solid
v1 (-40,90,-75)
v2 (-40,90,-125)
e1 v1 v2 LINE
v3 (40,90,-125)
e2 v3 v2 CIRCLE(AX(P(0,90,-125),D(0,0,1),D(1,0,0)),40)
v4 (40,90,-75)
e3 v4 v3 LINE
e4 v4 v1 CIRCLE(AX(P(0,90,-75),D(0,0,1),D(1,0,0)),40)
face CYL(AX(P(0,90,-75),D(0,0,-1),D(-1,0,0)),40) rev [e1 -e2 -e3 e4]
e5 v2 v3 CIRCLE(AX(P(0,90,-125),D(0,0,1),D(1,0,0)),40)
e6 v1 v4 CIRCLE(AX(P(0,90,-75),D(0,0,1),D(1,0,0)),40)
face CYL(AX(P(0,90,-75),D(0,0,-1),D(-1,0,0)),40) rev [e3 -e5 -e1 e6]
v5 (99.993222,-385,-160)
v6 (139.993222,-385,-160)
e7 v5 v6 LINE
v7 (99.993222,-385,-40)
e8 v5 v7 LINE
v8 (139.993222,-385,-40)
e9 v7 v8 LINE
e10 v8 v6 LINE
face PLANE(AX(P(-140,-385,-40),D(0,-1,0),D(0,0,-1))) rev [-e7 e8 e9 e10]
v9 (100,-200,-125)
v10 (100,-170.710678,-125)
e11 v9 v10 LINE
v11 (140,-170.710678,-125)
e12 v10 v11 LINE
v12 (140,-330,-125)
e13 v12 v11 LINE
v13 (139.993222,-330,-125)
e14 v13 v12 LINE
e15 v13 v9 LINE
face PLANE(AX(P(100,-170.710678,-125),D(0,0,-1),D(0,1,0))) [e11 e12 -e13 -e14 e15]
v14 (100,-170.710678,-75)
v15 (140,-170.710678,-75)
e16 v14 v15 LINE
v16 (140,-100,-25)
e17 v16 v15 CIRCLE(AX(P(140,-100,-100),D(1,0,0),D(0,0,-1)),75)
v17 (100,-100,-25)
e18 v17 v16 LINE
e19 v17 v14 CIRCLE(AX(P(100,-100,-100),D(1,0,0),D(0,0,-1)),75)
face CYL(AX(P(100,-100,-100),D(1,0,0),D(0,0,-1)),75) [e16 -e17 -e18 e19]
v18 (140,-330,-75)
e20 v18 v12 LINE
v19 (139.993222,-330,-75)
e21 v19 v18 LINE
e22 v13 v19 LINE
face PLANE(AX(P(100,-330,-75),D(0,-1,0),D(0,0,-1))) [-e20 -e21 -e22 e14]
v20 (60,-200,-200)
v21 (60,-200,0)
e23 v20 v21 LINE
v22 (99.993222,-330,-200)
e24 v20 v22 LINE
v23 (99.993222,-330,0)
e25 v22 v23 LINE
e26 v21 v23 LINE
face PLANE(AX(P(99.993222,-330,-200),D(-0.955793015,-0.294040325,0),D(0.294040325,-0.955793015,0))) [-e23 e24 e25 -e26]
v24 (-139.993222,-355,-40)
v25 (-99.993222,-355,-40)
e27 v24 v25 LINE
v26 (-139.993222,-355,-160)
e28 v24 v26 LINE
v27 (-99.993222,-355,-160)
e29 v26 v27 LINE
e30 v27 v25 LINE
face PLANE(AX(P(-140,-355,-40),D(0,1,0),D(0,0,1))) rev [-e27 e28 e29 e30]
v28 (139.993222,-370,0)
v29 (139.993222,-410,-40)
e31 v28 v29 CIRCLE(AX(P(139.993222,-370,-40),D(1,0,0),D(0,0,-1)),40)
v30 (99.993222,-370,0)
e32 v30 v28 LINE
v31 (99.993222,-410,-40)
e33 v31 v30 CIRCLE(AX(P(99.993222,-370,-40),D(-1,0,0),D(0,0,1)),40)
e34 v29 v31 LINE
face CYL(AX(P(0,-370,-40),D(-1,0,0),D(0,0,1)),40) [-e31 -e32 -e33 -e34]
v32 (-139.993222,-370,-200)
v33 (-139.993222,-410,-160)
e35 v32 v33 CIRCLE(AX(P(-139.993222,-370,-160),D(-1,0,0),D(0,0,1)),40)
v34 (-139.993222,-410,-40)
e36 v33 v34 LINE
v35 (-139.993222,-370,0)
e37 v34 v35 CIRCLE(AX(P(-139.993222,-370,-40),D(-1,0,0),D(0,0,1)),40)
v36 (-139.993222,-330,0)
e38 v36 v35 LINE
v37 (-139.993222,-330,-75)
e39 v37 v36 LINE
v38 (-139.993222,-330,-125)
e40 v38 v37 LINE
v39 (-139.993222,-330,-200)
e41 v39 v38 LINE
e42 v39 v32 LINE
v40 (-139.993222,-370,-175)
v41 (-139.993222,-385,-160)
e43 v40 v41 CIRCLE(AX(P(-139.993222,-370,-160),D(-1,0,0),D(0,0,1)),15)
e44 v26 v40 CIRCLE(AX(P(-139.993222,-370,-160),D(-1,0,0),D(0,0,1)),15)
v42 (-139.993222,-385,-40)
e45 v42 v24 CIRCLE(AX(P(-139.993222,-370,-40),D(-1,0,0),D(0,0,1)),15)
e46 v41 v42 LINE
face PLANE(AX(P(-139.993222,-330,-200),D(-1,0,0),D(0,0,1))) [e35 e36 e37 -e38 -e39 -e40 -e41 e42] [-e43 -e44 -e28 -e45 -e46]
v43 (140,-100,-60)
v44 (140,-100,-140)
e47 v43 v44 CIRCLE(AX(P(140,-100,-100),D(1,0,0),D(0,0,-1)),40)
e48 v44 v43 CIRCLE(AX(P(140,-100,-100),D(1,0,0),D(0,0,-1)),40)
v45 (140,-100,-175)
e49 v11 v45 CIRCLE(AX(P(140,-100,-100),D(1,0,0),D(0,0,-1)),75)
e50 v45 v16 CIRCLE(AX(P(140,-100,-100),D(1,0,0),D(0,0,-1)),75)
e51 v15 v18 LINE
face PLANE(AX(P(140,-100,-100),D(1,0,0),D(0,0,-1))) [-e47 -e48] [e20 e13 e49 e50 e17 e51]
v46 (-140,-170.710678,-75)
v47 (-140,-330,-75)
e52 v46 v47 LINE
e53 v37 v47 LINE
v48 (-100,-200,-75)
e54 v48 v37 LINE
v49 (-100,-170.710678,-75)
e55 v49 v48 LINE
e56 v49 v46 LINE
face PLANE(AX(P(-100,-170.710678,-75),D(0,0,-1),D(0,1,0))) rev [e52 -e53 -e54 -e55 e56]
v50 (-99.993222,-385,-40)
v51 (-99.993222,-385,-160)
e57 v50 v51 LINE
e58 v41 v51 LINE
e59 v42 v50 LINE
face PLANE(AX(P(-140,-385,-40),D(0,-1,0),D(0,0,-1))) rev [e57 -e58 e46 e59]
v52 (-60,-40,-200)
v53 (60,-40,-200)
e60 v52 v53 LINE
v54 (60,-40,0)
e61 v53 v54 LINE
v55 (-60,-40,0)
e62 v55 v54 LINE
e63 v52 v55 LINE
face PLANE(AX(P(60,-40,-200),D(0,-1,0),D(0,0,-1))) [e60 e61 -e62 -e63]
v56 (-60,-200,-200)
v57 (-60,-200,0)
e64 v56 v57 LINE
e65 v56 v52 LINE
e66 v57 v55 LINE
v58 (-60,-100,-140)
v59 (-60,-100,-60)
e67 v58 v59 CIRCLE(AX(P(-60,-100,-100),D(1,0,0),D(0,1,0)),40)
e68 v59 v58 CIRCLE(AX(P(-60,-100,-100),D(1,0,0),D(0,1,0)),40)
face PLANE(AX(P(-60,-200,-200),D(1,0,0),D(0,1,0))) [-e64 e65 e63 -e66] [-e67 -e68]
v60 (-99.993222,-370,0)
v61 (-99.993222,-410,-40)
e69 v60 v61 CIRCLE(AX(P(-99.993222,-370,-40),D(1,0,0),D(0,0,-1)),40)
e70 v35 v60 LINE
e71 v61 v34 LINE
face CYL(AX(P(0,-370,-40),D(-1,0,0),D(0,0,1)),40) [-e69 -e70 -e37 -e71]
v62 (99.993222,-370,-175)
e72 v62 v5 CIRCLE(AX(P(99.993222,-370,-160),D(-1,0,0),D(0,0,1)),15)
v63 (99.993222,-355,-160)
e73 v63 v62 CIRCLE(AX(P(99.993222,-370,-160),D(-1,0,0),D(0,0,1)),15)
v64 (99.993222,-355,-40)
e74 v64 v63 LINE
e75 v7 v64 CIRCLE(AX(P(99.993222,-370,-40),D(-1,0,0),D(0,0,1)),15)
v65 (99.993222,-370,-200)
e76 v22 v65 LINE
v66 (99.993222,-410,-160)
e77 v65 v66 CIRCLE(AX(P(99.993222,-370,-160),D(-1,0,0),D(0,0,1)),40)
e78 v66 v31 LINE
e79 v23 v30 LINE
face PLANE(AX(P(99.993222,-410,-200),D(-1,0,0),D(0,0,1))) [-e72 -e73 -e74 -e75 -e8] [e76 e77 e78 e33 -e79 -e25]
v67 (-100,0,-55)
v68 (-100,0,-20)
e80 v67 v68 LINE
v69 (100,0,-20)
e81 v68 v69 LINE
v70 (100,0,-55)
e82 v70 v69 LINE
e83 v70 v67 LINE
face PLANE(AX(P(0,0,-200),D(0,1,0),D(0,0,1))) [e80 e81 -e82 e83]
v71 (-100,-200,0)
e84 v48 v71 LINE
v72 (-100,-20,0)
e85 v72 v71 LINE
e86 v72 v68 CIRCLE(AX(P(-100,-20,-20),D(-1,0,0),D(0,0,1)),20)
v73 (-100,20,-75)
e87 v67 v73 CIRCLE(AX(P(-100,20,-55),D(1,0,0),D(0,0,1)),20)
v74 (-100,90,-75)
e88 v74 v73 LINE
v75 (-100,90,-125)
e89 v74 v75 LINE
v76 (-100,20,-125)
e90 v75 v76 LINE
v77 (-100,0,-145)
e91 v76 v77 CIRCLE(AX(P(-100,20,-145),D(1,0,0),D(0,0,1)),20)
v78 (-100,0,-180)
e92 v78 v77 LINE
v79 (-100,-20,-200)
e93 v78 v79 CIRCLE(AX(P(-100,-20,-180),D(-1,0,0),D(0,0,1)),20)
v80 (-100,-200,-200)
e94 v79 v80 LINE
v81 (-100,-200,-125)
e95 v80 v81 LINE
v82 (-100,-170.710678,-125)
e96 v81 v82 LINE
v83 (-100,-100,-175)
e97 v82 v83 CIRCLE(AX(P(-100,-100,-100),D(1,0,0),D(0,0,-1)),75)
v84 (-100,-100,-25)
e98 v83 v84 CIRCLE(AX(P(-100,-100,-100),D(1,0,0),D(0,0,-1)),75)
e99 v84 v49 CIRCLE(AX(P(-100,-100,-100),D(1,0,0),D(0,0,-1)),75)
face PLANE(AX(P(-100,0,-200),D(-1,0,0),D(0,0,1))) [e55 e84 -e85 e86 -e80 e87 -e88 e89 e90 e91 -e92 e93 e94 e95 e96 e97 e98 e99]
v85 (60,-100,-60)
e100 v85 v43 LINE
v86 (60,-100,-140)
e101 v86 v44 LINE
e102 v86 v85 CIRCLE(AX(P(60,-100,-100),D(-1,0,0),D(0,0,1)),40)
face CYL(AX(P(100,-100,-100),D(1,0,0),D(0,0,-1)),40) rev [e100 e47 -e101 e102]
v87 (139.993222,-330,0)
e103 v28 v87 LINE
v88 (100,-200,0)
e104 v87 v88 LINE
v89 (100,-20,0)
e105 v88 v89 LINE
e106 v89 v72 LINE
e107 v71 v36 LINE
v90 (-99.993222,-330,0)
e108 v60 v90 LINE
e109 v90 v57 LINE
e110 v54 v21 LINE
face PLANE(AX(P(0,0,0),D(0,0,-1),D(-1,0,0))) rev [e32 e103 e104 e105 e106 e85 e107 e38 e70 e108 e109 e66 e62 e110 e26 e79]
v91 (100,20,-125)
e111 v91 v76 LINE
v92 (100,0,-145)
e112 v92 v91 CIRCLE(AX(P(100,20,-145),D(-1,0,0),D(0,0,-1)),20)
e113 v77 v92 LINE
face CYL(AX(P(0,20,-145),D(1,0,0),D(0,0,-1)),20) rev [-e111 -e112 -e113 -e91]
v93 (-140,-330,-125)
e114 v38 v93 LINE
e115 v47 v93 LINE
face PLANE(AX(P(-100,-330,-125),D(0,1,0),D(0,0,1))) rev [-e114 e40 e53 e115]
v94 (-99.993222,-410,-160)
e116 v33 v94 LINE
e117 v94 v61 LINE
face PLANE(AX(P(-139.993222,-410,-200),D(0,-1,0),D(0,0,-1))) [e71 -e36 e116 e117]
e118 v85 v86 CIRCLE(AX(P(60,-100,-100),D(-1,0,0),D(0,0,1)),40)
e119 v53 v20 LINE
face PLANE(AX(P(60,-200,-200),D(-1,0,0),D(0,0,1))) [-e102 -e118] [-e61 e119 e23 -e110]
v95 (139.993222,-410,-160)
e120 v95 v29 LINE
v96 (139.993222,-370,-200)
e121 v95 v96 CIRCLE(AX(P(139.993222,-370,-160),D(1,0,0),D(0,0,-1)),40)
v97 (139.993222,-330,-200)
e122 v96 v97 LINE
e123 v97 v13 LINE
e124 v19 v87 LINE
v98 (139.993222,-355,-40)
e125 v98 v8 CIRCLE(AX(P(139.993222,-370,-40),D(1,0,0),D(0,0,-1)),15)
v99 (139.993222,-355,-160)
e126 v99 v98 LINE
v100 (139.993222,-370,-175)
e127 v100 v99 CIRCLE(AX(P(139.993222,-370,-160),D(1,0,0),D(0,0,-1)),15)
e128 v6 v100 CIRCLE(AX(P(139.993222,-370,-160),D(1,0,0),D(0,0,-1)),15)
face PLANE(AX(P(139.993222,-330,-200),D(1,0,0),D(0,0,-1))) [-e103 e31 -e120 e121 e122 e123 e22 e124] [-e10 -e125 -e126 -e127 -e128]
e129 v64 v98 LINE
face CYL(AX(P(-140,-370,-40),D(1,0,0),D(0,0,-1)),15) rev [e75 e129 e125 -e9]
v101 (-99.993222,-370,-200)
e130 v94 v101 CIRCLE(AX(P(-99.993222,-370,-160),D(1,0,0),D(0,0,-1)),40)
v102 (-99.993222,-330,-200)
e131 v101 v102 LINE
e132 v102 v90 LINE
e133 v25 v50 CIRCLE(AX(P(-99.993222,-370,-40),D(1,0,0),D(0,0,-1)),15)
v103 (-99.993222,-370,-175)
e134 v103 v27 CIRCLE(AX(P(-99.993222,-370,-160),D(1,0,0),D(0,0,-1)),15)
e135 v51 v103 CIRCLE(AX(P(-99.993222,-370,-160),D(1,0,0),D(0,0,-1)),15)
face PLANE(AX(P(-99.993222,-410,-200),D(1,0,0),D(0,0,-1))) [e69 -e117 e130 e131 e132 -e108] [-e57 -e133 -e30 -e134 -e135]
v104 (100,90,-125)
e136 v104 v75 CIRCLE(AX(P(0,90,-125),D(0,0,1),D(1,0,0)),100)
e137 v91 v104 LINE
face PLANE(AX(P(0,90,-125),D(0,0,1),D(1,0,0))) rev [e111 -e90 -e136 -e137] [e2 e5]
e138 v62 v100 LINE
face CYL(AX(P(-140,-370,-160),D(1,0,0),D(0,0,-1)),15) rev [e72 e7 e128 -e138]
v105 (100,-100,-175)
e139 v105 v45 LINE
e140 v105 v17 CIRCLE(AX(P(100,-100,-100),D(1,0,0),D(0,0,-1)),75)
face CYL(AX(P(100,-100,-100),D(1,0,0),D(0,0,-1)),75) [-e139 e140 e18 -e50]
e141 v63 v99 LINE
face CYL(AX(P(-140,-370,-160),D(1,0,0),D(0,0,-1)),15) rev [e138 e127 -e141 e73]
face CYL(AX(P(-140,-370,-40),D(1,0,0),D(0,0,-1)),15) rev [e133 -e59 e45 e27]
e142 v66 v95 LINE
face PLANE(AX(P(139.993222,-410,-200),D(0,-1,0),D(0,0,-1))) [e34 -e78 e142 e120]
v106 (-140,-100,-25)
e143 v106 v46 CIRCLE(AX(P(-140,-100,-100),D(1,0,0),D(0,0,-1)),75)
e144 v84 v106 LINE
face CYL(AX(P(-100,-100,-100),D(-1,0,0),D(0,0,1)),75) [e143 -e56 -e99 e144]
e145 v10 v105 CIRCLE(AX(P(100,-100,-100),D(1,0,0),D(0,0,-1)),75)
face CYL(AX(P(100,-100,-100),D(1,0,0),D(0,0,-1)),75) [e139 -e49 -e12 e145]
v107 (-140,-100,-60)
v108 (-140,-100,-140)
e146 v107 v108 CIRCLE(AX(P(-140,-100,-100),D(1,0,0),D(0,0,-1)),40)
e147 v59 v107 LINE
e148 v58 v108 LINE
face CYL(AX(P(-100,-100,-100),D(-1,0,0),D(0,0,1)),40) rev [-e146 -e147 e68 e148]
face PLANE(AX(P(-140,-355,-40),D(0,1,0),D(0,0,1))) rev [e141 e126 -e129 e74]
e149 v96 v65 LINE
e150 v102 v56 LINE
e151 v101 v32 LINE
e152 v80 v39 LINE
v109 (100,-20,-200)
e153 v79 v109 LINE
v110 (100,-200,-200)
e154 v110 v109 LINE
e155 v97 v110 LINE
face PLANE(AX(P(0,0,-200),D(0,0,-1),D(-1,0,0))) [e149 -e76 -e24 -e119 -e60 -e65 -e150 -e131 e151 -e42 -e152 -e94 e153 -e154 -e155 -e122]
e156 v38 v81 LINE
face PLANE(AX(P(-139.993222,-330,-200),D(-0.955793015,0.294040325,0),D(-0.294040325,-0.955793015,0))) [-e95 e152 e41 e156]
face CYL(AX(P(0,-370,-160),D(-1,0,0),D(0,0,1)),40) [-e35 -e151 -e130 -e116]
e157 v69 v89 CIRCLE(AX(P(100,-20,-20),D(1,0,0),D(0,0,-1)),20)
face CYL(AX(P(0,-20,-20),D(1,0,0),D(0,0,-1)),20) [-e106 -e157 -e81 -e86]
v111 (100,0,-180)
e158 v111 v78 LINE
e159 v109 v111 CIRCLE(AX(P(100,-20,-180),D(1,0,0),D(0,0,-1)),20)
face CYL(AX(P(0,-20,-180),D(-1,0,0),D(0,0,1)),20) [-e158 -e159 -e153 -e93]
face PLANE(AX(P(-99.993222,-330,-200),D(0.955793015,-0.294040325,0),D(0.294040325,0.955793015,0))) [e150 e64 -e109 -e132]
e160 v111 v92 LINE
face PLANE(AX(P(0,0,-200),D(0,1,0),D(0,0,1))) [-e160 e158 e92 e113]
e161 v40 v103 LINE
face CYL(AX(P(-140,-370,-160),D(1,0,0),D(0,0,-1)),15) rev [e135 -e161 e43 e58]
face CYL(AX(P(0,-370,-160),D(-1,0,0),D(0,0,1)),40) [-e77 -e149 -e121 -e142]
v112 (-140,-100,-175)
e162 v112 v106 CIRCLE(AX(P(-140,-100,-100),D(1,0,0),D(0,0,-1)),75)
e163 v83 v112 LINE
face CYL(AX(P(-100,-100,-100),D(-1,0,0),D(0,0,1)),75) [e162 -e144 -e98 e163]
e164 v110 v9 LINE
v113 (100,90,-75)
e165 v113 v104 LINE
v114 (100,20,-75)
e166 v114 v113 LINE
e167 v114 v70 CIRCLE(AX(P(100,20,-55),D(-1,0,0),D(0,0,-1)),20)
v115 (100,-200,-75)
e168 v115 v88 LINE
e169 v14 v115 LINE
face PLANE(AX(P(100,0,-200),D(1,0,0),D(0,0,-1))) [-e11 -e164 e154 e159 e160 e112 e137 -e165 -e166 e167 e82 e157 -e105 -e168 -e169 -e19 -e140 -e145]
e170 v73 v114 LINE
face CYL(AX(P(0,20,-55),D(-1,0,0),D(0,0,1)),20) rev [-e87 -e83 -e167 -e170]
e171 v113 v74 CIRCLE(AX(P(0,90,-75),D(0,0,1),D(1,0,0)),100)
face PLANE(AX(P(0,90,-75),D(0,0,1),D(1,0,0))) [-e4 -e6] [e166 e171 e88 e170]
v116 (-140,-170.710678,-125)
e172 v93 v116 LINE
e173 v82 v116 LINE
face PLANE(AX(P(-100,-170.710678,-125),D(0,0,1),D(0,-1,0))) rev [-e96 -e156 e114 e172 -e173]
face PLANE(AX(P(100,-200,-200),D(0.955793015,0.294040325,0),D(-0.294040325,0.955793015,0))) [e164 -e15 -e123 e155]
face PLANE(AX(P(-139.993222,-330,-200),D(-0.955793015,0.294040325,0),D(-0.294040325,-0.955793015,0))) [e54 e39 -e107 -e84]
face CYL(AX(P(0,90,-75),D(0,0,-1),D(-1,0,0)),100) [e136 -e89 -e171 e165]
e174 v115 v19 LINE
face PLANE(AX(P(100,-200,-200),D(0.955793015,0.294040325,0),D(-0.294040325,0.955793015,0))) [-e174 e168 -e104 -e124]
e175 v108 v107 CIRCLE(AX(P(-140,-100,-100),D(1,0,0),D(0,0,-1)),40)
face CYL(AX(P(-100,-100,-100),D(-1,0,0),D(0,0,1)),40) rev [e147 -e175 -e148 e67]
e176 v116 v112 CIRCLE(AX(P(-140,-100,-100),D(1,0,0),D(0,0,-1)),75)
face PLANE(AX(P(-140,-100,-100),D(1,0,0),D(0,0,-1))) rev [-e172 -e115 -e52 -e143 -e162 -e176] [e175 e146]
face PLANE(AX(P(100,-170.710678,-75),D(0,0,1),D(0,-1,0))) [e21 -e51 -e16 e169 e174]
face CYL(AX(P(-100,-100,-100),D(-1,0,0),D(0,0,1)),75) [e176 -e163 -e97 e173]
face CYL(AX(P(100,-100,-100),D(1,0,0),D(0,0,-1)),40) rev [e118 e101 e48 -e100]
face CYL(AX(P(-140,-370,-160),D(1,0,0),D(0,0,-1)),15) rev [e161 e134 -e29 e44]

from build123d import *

# Parameters (mm, degrees)
FORK_BODY_DEPTH         = 200
SIDE_BOSS_A_SKETCH_R    = 40
SIDE_BOSS_A_DEPTH       = 40
SIDE_START              = 40
SIDE_BOSS_B_SKETCH_R    = 40
SIDE_BOSS_B_DEPTH       = 40
PIVOT_BORE_SKETCH_R     = 40
PIVOT_BORE_80_DEPTH     = 516.460958754
TOP_LUG_SKETCH_R        = 40
TOP_LUG_DEPTH           = 25
TOP_LUG_BLEND_R20_R     = 20
FORK_FILLET_R40_A_R     = 40
FORK_FILLET_R40_B_R     = 40
FORK_FILLET_R40_C_R     = 40
FORK_FILLET_R40_D_R     = 40
FOOT_SLOTS_15X120_DEPTH = 536.253402042


with BuildPart() as part:
    # Fork Profile Sketch → Fork Body (new body)
    with BuildSketch(Plane.XY):
        Polygon((0, 0), (-100, 0), (-100, -200), (-139.993222056, -330), (-139.993222056, -410), (-99.993222056, -410), (-99.993222056, -330), (-60, -200), (-60, -40), (60, -40), (60, -200), (99.993222056, -330), (99.993222056, -410), (139.993222056, -410), (139.993222056, -330), (100, -200), (100, 0), align=None)
    extrude(amount=-FORK_BODY_DEPTH)

    # Side Boss A Sketch → Side Boss A (add)
    with BuildSketch(Plane(origin=(140, 0, 0), x_dir=(0, 0, -1), z_dir=(1, 0, 0))):
        with BuildLine():
            Line((75, -170.710678119), (75, -330))
            Line((75, -330), (125, -330))
            Line((125, -330), (125, -170.710678119))
            ThreePointArc((125, -170.710678119), (100, -25), (75, -170.710678119))
        make_face()
        with Locations((100, -100)):
            Circle(SIDE_BOSS_A_SKETCH_R, mode=Mode.SUBTRACT)
    extrude(amount=-SIDE_BOSS_A_DEPTH)

    # Side Boss B Sketch → Side Boss B (add)
    with BuildSketch(Plane(origin=(-140, 0, 0), x_dir=(0, 0, -1), z_dir=(1, 0, 0)).offset(SIDE_START)):
        with BuildLine():
            Line((125, -170.710678119), (125, -330))
            Line((125, -330), (75, -330))
            Line((75, -330), (75, -170.710678119))
            ThreePointArc((75, -170.710678119), (100, -25), (125, -170.710678119))
        make_face()
        with Locations((100, -100)):
            Circle(SIDE_BOSS_B_SKETCH_R, mode=Mode.SUBTRACT)
    extrude(amount=-SIDE_BOSS_B_DEPTH)

    # Pivot Bore Sketch → Pivot Bore Ø80 (cut, through all)
    with BuildSketch(Plane(origin=(100, 0, 0), x_dir=(0, 0, -1), z_dir=(1, 0, 0))):
        with Locations((100, -100)):
            Circle(PIVOT_BORE_SKETCH_R)
    extrude(amount=-PIVOT_BORE_80_DEPTH, mode=Mode.SUBTRACT)

    # Top Lug Sketch → Top Lug (add, symmetric)
    with BuildSketch(Plane.XY.offset(-100)):
        with BuildLine():
            Line((-100, 90), (-100, 0))
            Line((-100, 0), (100, 0))
            Line((100, 0), (100, 90))
            ThreePointArc((100, 90), (0, 190), (-100, 90))
        make_face()
        with Locations((0, 90)):
            Circle(TOP_LUG_SKETCH_R, mode=Mode.SUBTRACT)
    extrude(amount=TOP_LUG_DEPTH, both=True)

    # Top Lug Blend R20
    top_lug_blend_r20_edges = [part.edges().sort_by_distance(p)[0] for p in [
        (0, 0, -75),
        (0, 0, -125),
        (0, 0, 0),
        (0, 0, -200),
    ]]
    fillet(top_lug_blend_r20_edges, radius=TOP_LUG_BLEND_R20_R)

    # Fork Fillet R40 A
    fork_fillet_r40_a_edges = [part.edges().sort_by_distance(p)[0] for p in [
        (119.993222056, -410, 0),
    ]]
    fillet(fork_fillet_r40_a_edges, radius=FORK_FILLET_R40_A_R)

    # Fork Fillet R40 B
    fork_fillet_r40_b_edges = [part.edges().sort_by_distance(p)[0] for p in [
        (119.993222056, -410, -200),
    ]]
    fillet(fork_fillet_r40_b_edges, radius=FORK_FILLET_R40_B_R)

    # Fork Fillet R40 C
    fork_fillet_r40_c_edges = [part.edges().sort_by_distance(p)[0] for p in [
        (-119.993222056, -410, 0),
    ]]
    fillet(fork_fillet_r40_c_edges, radius=FORK_FILLET_R40_C_R)

    # Fork Fillet R40 D
    fork_fillet_r40_d_edges = [part.edges().sort_by_distance(p)[0] for p in [
        (-119.993222056, -410, -200),
    ]]
    fillet(fork_fillet_r40_d_edges, radius=FORK_FILLET_R40_D_R)

    # Foot Slot Sketch → Foot Slots 15x120 (cut, through all)
    with BuildSketch(Plane(origin=(139.993222056, 0, 0), x_dir=(0, 0, -1), z_dir=(1, 0, 0))):
        with BuildLine():
            Line((40, -355), (160, -355))
            ThreePointArc((160, -355), (175, -370), (160, -385))
            Line((160, -385), (40, -385))
            ThreePointArc((40, -385), (25, -370), (40, -355))
        make_face()
    extrude(amount=-FOOT_SLOTS_15X120_DEPTH, mode=Mode.SUBTRACT)


solid = part.part
